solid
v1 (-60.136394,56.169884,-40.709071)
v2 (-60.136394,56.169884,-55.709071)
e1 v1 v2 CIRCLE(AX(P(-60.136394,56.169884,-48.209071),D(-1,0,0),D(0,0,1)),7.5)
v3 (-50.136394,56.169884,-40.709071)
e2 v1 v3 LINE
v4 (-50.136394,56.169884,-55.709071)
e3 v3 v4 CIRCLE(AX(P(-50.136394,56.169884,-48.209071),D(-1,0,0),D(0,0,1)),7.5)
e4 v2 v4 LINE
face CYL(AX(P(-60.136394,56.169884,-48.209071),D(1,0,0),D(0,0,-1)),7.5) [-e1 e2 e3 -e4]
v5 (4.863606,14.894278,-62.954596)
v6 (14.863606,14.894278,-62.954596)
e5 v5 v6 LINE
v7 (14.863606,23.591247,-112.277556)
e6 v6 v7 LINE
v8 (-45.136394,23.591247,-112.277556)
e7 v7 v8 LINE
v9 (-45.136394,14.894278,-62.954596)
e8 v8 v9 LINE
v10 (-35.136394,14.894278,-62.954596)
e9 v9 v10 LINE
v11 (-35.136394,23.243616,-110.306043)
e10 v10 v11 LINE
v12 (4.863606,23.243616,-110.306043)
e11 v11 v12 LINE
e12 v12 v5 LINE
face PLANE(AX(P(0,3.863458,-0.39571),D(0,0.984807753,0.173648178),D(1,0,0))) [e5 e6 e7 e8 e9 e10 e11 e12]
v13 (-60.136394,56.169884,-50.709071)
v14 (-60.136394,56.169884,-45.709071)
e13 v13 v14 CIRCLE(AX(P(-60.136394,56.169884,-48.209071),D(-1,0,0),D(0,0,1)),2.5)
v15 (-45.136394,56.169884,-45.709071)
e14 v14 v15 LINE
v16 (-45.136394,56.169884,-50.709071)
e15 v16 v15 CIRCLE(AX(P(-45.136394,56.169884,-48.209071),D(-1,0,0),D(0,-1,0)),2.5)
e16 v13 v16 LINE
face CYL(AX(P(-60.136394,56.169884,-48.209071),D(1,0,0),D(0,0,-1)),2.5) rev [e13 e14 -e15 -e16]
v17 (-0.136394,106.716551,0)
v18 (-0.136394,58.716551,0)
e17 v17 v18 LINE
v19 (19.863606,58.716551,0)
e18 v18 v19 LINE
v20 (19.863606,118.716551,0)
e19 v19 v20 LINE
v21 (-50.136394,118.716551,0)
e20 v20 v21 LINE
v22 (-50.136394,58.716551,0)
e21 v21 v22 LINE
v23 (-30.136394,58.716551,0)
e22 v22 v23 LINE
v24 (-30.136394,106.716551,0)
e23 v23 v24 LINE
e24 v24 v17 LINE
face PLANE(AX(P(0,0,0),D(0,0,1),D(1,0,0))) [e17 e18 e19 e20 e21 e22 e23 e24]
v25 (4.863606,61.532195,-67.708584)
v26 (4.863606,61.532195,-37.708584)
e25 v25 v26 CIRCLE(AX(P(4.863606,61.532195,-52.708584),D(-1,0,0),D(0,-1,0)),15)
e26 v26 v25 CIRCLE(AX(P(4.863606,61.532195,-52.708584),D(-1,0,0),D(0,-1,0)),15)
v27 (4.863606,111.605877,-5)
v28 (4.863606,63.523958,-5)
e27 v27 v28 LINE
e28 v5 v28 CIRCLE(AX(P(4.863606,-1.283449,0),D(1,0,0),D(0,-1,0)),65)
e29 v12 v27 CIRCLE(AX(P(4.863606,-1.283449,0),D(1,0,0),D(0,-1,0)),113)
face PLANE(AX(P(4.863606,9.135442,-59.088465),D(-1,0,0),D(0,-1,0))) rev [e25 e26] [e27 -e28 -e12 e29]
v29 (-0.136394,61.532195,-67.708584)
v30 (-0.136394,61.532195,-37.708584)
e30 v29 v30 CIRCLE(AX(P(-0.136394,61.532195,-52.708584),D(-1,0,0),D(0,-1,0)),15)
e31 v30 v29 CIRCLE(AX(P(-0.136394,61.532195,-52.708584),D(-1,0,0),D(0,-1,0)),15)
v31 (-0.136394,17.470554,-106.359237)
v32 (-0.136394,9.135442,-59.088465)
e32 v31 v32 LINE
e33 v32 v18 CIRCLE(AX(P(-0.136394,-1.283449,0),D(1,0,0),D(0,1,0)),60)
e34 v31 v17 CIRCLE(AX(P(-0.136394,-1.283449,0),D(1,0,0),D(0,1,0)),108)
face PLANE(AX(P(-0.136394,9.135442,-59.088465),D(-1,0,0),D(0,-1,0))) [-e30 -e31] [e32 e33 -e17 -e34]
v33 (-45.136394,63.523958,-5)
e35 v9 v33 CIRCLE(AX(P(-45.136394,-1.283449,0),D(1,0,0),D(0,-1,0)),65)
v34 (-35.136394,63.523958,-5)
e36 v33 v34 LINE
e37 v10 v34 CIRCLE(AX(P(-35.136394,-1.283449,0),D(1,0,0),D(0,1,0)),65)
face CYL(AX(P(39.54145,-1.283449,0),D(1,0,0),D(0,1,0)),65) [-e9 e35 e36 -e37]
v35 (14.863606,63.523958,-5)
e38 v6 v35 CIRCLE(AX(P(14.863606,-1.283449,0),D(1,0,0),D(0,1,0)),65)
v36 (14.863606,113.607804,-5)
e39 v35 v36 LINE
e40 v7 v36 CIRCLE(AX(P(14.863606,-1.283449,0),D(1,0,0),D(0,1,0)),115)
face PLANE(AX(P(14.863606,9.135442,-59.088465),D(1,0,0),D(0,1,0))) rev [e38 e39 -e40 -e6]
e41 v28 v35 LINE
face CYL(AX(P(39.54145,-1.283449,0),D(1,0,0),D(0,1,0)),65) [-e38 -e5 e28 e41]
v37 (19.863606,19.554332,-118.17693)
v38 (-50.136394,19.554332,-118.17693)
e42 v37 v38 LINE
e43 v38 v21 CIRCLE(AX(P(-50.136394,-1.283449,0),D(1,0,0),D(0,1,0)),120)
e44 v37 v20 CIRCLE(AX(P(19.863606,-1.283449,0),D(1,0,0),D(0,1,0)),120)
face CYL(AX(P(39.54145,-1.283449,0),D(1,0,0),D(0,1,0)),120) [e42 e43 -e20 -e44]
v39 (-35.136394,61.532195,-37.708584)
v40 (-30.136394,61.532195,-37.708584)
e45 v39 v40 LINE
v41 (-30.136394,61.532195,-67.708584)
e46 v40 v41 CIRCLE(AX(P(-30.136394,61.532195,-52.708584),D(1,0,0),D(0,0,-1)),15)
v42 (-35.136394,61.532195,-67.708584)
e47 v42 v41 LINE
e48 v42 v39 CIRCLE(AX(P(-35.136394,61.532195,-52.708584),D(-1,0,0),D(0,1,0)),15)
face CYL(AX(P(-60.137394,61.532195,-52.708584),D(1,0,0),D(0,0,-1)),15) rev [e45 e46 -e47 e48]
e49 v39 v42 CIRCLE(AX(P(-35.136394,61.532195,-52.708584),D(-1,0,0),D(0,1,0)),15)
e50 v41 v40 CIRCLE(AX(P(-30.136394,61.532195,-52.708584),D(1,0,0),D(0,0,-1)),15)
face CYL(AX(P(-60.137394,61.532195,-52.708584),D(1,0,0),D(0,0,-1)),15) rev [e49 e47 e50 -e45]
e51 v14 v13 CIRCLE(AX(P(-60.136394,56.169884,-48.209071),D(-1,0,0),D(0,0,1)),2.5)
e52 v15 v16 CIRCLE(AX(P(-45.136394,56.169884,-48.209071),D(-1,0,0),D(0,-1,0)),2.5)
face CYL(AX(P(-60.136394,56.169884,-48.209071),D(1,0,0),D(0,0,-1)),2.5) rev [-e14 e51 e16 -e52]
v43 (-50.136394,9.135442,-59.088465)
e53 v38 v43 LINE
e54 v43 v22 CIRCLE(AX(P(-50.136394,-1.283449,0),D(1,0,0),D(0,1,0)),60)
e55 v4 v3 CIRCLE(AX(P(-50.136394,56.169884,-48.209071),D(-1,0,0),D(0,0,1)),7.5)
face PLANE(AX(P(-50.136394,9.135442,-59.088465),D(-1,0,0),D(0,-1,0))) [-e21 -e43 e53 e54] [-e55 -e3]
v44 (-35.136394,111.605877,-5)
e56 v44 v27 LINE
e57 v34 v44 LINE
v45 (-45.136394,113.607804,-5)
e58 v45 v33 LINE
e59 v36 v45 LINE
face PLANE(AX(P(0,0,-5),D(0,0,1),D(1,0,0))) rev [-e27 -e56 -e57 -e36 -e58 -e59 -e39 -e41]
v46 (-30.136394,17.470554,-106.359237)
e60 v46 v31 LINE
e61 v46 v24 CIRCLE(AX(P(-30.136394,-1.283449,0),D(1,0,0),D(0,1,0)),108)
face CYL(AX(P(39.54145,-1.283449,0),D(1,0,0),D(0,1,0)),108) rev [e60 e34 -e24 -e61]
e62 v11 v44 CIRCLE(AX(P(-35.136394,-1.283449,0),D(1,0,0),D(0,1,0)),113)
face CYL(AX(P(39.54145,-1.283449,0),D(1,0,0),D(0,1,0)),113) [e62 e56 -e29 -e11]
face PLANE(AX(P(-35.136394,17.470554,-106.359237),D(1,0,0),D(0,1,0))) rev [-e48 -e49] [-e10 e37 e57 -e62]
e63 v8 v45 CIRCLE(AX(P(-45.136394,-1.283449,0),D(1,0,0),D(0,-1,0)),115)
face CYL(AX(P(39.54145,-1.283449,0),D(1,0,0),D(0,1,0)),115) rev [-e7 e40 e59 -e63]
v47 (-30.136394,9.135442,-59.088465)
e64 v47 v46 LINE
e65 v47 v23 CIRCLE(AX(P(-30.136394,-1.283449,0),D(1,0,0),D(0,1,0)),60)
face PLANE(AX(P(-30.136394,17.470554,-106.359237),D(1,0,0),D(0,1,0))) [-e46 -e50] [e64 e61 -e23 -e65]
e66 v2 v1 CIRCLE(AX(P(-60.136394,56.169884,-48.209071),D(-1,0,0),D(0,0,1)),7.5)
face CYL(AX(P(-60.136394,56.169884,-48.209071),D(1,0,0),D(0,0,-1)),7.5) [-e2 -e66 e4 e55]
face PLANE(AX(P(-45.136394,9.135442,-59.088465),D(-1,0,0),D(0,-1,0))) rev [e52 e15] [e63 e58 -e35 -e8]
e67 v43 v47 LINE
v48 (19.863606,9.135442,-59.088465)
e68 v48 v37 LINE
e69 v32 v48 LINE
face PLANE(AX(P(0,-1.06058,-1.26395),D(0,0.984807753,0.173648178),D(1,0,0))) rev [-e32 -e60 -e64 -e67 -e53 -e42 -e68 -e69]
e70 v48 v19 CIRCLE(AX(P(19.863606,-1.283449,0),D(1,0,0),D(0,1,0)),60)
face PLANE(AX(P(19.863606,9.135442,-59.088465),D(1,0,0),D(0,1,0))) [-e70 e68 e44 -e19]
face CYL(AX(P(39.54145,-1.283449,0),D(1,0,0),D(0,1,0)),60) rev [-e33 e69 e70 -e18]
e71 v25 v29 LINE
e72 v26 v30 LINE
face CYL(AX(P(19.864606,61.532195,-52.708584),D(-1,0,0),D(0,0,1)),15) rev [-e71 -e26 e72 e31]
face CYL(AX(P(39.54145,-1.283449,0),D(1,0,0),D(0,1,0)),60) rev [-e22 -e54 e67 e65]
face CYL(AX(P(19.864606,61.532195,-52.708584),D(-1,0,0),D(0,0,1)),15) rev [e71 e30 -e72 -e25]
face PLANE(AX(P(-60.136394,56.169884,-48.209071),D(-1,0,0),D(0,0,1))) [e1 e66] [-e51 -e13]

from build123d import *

# Parameters (mm, degrees)
REVOLVE1_ANGLE                 = 80
SKETCH3_R                      = 7.5
BOSS_EXTRUDE1_DEPTH            = 10
SHELL3_T                       = -5
CUT_EXTRUDE1_REACH             = 176.812
SKETCH4_R                      = 15
CUT_EXTRUDE1_DIRECTION_2_REACH = 176.812


with BuildPart() as part:
    # Sketch1 → Revolve1 (revolve)
    with BuildSketch(Plane.XY):
        Polygon((-0.136394071, 58.716551136), (19.863605929, 58.716551136), (19.863605929, 118.716551136), (-50.136394071, 118.716551136), (-50.136394071, 58.716551136), (-30.136394071, 58.716551136), (-30.136394071, 106.716551136), (-0.136394071, 106.716551136), align=None)
    revolve(axis=Axis((39.541450035, -1.283448864, 0), (-1, 0, 0)), revolution_arc=REVOLVE1_ANGLE)

    # Sketch3 → Boss-Extrude1 (add)
    with BuildSketch(Plane.ZY.offset(50.136394071)):
        with Locations((-48.209070726, 56.16988437)):
            Circle(SKETCH3_R)
    extrude(amount=BOSS_EXTRUDE1_DEPTH)

    # Shell3
    shell3_openings = [part.faces().sort_by_distance(p)[0] for p in [
        (-60.136394071, 56.16988437, -48.209070726),
    ]]
    offset(amount=SHELL3_T, openings=shell3_openings, kind=Kind.INTERSECTION)

    # Sketch4 → Cut-Extrude1 (cut, up to next)
    with BuildSketch(Plane(origin=(-30.136394071, 0, 0), x_dir=(0, 0, -1), z_dir=(1, 0, 0)), mode=Mode.PRIVATE) as cut_extrude1_sk1:
        with Locations(Location((52.708583994, 61.532195472, 0), (0, 0, 270))):
            Circle(SKETCH4_R)
    cut_extrude1_tool1 = extrude(cut_extrude1_sk1.sketch, amount=-CUT_EXTRUDE1_REACH, mode=Mode.PRIVATE) & part.part
    add(cut_extrude1_tool1.solids().sort_by_distance((-30.136394, 61.532195, -52.708584))[0], mode=Mode.SUBTRACT)

    # Sketch4 → Cut-Extrude1 direction 2 (cut, up to next)
    with BuildSketch(Plane(origin=(-30.136394071, 0, 0), x_dir=(0, 0, -1), z_dir=(1, 0, 0)), mode=Mode.PRIVATE) as cut_extrude1_direction_2_sk1:
        with Locations(Location((52.708583994, 61.532195472, 0), (0, 0, 270))):
            Circle(SKETCH4_R)
    cut_extrude1_direction_2_tool1 = extrude(cut_extrude1_direction_2_sk1.sketch, amount=CUT_EXTRUDE1_DIRECTION_2_REACH, mode=Mode.PRIVATE) & part.part
    add(cut_extrude1_direction_2_tool1.solids().sort_by_distance((-30.136394, 61.532195, -52.708584))[0], mode=Mode.SUBTRACT)


solid = part.part
